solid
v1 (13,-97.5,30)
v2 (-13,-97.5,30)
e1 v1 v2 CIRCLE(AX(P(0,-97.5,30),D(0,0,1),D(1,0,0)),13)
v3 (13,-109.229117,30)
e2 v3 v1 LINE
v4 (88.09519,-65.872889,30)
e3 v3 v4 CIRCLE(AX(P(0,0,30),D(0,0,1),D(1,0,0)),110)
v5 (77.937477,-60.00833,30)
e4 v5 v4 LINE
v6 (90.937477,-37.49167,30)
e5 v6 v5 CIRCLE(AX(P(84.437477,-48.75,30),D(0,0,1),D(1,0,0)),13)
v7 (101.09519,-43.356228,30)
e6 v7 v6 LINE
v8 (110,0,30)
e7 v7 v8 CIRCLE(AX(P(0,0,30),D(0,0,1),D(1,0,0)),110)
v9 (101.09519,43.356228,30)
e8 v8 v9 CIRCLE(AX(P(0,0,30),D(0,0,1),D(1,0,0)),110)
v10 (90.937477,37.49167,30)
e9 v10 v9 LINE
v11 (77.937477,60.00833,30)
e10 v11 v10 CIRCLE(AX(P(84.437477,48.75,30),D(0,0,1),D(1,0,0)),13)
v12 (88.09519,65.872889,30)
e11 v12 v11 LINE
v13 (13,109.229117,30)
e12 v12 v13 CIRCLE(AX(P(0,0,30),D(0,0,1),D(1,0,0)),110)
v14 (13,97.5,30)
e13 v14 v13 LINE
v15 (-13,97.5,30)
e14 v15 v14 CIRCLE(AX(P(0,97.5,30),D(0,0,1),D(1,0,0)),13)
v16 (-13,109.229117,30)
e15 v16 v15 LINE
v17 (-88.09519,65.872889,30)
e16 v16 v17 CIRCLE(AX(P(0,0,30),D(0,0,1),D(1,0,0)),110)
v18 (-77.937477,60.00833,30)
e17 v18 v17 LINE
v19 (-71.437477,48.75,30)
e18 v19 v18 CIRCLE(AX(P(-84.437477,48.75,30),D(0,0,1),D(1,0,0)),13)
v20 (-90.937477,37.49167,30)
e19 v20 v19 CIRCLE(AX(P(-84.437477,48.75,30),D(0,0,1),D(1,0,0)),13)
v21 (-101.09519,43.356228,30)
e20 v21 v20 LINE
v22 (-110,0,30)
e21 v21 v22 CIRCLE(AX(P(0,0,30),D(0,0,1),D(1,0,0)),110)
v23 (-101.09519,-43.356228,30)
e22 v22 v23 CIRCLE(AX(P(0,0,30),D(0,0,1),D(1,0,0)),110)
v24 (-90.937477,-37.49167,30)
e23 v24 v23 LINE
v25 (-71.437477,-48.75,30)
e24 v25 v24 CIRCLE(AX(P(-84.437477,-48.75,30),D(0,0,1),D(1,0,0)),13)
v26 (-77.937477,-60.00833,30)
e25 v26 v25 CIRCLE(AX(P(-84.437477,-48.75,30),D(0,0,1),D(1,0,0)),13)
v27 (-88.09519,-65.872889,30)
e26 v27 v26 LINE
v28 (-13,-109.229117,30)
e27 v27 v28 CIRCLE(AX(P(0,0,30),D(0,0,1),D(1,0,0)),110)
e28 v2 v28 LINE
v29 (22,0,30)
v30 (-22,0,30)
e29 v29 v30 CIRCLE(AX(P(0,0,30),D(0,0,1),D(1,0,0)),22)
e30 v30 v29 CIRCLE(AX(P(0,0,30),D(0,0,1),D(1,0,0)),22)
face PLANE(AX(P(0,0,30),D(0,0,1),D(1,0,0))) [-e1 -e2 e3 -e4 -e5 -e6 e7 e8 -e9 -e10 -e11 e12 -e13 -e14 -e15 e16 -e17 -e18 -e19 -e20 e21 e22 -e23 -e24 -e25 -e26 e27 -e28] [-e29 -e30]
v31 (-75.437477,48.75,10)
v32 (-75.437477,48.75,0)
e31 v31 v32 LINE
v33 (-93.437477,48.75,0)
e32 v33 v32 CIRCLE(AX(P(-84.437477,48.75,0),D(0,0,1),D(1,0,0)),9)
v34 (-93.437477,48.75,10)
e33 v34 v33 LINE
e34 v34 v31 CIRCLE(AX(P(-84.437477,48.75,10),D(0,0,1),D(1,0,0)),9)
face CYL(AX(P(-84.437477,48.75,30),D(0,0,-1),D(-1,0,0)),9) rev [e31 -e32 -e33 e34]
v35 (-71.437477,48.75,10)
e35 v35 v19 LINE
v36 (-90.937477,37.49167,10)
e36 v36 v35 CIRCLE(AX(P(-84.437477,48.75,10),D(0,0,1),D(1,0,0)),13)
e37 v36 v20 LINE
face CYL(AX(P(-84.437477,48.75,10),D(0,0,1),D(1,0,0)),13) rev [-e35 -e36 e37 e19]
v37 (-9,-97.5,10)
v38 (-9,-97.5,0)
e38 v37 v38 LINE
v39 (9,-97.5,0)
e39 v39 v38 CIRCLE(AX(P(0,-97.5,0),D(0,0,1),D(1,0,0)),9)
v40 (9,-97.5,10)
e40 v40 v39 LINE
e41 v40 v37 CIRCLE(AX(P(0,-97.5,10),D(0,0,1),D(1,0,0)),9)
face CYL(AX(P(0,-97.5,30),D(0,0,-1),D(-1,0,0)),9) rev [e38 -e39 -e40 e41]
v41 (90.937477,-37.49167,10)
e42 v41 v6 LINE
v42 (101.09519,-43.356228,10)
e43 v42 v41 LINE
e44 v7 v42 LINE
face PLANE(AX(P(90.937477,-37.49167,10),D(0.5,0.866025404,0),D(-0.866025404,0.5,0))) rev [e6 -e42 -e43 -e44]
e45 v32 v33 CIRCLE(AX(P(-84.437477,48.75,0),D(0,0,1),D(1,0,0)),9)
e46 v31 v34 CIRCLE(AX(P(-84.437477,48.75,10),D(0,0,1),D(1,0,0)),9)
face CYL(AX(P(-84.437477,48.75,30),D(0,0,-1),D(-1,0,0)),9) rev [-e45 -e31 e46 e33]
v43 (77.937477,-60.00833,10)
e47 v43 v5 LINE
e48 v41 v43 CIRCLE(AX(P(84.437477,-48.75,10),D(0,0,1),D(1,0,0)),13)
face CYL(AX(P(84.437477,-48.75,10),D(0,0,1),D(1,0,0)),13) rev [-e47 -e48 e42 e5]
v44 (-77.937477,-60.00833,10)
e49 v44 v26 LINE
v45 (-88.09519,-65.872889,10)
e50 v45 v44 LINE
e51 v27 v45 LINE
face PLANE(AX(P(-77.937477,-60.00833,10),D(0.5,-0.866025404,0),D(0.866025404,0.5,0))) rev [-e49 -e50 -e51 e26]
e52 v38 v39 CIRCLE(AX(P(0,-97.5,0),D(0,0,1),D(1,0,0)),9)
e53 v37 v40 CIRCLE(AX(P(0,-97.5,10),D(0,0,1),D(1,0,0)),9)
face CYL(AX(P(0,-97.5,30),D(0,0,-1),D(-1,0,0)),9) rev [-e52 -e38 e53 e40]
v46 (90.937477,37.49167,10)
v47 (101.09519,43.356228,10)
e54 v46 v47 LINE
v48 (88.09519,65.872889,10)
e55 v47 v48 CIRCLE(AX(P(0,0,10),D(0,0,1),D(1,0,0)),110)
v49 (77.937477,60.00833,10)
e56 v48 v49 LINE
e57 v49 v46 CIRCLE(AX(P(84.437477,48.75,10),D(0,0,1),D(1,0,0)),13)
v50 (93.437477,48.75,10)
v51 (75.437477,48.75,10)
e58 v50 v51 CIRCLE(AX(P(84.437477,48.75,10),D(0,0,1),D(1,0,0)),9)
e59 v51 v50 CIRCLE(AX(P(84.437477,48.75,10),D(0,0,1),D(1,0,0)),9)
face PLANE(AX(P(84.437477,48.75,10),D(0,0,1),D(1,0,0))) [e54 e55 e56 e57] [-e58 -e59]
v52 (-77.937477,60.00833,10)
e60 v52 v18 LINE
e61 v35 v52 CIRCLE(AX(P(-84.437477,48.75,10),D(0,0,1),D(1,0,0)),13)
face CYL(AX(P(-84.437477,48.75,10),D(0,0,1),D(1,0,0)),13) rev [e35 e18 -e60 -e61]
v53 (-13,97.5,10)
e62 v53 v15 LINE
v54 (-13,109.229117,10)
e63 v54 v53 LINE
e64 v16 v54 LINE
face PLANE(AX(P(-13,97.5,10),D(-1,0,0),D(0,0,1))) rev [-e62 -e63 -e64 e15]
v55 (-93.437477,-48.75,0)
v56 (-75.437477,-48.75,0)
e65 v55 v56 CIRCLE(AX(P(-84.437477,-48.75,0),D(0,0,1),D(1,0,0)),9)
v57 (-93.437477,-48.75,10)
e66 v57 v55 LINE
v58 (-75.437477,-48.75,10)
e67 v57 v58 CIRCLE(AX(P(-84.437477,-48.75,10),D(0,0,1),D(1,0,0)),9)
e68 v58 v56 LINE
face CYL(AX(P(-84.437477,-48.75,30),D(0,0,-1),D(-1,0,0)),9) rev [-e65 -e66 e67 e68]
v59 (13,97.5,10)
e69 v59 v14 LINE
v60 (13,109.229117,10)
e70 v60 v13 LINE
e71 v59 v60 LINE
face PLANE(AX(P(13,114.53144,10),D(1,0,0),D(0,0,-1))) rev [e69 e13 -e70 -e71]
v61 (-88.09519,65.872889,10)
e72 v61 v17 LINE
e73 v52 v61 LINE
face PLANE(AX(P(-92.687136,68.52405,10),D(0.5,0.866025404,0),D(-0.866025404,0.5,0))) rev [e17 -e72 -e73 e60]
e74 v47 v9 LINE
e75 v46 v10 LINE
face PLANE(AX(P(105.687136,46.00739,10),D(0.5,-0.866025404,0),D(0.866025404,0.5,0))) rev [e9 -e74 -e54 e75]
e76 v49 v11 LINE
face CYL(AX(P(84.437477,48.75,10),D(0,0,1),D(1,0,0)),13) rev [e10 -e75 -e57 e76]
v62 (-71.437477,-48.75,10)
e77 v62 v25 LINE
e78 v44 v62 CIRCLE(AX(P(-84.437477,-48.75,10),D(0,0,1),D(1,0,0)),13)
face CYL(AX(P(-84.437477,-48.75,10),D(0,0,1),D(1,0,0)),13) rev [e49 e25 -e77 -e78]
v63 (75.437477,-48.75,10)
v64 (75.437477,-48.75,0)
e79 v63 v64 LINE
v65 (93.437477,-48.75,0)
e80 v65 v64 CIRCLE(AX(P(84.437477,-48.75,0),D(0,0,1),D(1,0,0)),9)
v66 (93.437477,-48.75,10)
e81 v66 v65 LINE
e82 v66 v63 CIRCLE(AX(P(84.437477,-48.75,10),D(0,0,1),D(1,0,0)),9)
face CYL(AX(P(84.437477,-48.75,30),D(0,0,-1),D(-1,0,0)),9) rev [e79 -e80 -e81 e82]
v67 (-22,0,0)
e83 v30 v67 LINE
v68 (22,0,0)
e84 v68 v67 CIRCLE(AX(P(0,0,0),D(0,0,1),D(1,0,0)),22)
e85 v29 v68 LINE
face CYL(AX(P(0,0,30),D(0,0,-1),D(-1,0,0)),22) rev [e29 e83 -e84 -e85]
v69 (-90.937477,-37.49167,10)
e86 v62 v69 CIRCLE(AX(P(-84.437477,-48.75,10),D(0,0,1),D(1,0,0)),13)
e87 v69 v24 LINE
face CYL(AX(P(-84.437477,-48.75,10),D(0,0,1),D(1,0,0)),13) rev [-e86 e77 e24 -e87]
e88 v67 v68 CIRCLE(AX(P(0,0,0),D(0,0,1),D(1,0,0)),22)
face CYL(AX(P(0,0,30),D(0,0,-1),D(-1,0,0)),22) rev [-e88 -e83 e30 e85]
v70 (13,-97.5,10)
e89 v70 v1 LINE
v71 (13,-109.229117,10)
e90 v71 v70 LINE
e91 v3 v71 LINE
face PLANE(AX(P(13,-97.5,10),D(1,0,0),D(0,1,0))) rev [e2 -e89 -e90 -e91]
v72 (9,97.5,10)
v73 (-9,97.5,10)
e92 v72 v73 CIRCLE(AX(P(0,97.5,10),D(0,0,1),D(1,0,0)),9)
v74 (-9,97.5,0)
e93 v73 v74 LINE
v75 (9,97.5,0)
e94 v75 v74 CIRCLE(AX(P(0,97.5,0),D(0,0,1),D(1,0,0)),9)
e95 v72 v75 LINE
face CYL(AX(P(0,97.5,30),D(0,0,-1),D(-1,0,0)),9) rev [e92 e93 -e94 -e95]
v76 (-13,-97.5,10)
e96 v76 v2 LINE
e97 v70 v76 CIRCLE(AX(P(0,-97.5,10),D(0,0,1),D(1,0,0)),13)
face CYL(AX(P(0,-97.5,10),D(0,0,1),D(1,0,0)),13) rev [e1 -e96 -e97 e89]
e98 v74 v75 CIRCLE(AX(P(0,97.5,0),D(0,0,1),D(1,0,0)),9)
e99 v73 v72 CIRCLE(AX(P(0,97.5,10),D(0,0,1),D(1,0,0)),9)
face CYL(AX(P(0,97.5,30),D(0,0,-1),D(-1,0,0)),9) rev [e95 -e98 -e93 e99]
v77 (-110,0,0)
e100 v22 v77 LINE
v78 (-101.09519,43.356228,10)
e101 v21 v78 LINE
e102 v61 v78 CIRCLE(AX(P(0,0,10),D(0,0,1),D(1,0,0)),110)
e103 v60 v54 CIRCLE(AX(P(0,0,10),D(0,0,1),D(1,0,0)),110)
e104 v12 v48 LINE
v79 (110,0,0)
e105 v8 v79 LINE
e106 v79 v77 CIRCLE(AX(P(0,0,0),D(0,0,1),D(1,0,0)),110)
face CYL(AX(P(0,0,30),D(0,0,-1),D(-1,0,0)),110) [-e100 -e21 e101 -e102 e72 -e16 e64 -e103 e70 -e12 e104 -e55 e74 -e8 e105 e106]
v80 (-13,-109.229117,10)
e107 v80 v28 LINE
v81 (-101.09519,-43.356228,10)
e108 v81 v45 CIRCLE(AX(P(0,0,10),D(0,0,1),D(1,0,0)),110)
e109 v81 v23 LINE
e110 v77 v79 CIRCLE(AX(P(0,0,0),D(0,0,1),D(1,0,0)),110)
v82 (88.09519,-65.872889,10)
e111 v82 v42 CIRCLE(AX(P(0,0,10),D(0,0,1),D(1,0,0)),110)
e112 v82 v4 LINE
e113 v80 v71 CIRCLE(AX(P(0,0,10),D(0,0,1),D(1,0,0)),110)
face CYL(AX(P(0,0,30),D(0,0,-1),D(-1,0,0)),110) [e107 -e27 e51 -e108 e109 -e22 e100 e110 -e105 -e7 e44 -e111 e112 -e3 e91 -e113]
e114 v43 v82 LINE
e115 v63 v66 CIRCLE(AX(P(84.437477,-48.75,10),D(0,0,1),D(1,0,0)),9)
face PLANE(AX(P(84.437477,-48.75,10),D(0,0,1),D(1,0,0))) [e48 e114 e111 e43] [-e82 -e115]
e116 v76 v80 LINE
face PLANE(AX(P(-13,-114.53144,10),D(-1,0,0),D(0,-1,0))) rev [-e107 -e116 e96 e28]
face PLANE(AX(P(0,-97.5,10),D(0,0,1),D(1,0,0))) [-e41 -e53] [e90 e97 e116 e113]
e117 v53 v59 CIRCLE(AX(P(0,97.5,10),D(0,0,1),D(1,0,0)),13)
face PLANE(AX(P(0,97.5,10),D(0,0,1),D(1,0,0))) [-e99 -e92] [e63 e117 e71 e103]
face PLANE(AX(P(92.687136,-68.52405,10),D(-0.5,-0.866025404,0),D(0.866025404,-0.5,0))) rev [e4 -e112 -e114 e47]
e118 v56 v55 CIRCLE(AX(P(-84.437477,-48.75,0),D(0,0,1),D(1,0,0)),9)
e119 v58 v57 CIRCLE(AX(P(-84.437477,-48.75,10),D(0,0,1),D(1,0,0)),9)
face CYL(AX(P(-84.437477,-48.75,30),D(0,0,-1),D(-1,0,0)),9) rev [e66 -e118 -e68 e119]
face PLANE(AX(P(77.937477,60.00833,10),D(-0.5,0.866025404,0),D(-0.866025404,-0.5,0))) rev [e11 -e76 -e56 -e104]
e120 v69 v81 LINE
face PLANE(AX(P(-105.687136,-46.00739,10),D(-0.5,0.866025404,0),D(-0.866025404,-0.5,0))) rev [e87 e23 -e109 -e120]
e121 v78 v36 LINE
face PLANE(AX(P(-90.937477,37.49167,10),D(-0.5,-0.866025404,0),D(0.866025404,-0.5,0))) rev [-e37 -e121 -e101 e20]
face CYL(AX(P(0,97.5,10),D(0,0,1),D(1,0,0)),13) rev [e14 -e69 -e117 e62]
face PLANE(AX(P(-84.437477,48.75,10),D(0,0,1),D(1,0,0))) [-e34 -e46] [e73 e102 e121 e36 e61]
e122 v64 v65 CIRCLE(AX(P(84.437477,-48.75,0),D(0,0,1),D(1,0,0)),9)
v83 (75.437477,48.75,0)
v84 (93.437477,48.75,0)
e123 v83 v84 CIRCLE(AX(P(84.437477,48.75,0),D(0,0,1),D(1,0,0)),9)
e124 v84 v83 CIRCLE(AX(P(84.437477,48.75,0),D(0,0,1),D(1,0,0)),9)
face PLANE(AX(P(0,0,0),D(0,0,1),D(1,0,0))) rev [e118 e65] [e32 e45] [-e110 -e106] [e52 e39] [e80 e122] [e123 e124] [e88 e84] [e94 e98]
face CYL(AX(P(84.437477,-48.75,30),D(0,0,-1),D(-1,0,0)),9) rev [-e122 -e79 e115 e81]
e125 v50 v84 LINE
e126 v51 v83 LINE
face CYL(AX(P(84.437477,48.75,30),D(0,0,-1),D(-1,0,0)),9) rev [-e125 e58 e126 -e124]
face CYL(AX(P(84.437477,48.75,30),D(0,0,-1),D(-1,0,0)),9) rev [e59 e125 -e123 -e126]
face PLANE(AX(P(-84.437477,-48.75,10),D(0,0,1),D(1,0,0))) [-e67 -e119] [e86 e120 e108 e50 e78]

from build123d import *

# Parameters (mm, degrees)
SKETCH1_R           = 110
SKETCH1_R_2         = 9
SKETCH1_R_3         = 22
BOSS_EXTRUDE1_DEPTH = 30
CUT_EXTRUDE1_DEPTH  = 20


with BuildPart() as part:
    # Sketch1 → Boss-Extrude1 (new body)
    with BuildSketch(Plane.XY):
        Circle(SKETCH1_R)
        with Locations((0, 97.5)):
            Circle(SKETCH1_R_2, mode=Mode.SUBTRACT)
        with Locations((84.437476869, 48.75)):
            Circle(SKETCH1_R_2, mode=Mode.SUBTRACT)
        with Locations((84.437476869, -48.75)):
            Circle(SKETCH1_R_2, mode=Mode.SUBTRACT)
        with Locations((0, -97.5)):
            Circle(SKETCH1_R_2, mode=Mode.SUBTRACT)
        with Locations((-84.437476869, -48.75)):
            Circle(SKETCH1_R_2, mode=Mode.SUBTRACT)
        with Locations((-84.437476869, 48.75)):
            Circle(SKETCH1_R_2, mode=Mode.SUBTRACT)
        Circle(SKETCH1_R_3, mode=Mode.SUBTRACT)
    extrude(amount=BOSS_EXTRUDE1_DEPTH)

    # Sketch2 → Cut-Extrude1 (cut)
    with BuildSketch(Plane.XY.offset(30)):
        with BuildLine():
            Line((-13, 97.5), (-13, 114.531439902))
            Line((-13, 114.531439902), (13, 114.531439902))
            Line((13, 114.531439902), (13, 97.5))
            ThreePointArc((13, 97.5), (0, 84.5), (-13, 97.5))
        make_face()
        with BuildLine():
            Line((105.687136487, 46.007389702), (90.937476869, 37.491669751))
            ThreePointArc((90.937476869, 37.491669751), (73.17914662, 42.25), (77.937476869, 60.008330249))
            Line((77.937476869, 60.008330249), (92.687136487, 68.5240502))
            Line((92.687136487, 68.5240502), (105.687136487, 46.007389702))
        make_face()
        with BuildLine():
            Line((92.687136487, -68.5240502), (77.937476869, -60.008330249))
            ThreePointArc((77.937476869, -60.008330249), (73.17914662, -42.25), (90.937476869, -37.491669751))
            Line((90.937476869, -37.491669751), (105.687136487, -46.007389702))
            Line((105.687136487, -46.007389702), (92.687136487, -68.5240502))
        make_face()
        with BuildLine():
            Line((-13, -114.531439902), (-13, -97.5))
            ThreePointArc((-13, -97.5), (0, -84.5), (13, -97.5))
            Line((13, -97.5), (13, -114.531439902))
            Line((13, -114.531439902), (-13, -114.531439902))
        make_face()
        with BuildLine():
            Line((-105.687136487, -46.007389702), (-90.937476869, -37.491669751))
            ThreePointArc((-90.937476869, -37.491669751), (-73.17914662, -42.25), (-77.937476869, -60.008330249))
            Line((-77.937476869, -60.008330249), (-92.687136487, -68.5240502))
            Line((-92.687136487, -68.5240502), (-105.687136487, -46.007389702))
        make_face()
        with BuildLine():
            Line((-92.687136487, 68.5240502), (-77.937476869, 60.008330249))
            ThreePointArc((-77.937476869, 60.008330249), (-73.17914662, 42.25), (-90.937476869, 37.491669751))
            Line((-90.937476869, 37.491669751), (-105.687136487, 46.007389702))
            Line((-105.687136487, 46.007389702), (-92.687136487, 68.5240502))
        make_face()
    extrude(amount=-CUT_EXTRUDE1_DEPTH, mode=Mode.SUBTRACT)


solid = part.part
